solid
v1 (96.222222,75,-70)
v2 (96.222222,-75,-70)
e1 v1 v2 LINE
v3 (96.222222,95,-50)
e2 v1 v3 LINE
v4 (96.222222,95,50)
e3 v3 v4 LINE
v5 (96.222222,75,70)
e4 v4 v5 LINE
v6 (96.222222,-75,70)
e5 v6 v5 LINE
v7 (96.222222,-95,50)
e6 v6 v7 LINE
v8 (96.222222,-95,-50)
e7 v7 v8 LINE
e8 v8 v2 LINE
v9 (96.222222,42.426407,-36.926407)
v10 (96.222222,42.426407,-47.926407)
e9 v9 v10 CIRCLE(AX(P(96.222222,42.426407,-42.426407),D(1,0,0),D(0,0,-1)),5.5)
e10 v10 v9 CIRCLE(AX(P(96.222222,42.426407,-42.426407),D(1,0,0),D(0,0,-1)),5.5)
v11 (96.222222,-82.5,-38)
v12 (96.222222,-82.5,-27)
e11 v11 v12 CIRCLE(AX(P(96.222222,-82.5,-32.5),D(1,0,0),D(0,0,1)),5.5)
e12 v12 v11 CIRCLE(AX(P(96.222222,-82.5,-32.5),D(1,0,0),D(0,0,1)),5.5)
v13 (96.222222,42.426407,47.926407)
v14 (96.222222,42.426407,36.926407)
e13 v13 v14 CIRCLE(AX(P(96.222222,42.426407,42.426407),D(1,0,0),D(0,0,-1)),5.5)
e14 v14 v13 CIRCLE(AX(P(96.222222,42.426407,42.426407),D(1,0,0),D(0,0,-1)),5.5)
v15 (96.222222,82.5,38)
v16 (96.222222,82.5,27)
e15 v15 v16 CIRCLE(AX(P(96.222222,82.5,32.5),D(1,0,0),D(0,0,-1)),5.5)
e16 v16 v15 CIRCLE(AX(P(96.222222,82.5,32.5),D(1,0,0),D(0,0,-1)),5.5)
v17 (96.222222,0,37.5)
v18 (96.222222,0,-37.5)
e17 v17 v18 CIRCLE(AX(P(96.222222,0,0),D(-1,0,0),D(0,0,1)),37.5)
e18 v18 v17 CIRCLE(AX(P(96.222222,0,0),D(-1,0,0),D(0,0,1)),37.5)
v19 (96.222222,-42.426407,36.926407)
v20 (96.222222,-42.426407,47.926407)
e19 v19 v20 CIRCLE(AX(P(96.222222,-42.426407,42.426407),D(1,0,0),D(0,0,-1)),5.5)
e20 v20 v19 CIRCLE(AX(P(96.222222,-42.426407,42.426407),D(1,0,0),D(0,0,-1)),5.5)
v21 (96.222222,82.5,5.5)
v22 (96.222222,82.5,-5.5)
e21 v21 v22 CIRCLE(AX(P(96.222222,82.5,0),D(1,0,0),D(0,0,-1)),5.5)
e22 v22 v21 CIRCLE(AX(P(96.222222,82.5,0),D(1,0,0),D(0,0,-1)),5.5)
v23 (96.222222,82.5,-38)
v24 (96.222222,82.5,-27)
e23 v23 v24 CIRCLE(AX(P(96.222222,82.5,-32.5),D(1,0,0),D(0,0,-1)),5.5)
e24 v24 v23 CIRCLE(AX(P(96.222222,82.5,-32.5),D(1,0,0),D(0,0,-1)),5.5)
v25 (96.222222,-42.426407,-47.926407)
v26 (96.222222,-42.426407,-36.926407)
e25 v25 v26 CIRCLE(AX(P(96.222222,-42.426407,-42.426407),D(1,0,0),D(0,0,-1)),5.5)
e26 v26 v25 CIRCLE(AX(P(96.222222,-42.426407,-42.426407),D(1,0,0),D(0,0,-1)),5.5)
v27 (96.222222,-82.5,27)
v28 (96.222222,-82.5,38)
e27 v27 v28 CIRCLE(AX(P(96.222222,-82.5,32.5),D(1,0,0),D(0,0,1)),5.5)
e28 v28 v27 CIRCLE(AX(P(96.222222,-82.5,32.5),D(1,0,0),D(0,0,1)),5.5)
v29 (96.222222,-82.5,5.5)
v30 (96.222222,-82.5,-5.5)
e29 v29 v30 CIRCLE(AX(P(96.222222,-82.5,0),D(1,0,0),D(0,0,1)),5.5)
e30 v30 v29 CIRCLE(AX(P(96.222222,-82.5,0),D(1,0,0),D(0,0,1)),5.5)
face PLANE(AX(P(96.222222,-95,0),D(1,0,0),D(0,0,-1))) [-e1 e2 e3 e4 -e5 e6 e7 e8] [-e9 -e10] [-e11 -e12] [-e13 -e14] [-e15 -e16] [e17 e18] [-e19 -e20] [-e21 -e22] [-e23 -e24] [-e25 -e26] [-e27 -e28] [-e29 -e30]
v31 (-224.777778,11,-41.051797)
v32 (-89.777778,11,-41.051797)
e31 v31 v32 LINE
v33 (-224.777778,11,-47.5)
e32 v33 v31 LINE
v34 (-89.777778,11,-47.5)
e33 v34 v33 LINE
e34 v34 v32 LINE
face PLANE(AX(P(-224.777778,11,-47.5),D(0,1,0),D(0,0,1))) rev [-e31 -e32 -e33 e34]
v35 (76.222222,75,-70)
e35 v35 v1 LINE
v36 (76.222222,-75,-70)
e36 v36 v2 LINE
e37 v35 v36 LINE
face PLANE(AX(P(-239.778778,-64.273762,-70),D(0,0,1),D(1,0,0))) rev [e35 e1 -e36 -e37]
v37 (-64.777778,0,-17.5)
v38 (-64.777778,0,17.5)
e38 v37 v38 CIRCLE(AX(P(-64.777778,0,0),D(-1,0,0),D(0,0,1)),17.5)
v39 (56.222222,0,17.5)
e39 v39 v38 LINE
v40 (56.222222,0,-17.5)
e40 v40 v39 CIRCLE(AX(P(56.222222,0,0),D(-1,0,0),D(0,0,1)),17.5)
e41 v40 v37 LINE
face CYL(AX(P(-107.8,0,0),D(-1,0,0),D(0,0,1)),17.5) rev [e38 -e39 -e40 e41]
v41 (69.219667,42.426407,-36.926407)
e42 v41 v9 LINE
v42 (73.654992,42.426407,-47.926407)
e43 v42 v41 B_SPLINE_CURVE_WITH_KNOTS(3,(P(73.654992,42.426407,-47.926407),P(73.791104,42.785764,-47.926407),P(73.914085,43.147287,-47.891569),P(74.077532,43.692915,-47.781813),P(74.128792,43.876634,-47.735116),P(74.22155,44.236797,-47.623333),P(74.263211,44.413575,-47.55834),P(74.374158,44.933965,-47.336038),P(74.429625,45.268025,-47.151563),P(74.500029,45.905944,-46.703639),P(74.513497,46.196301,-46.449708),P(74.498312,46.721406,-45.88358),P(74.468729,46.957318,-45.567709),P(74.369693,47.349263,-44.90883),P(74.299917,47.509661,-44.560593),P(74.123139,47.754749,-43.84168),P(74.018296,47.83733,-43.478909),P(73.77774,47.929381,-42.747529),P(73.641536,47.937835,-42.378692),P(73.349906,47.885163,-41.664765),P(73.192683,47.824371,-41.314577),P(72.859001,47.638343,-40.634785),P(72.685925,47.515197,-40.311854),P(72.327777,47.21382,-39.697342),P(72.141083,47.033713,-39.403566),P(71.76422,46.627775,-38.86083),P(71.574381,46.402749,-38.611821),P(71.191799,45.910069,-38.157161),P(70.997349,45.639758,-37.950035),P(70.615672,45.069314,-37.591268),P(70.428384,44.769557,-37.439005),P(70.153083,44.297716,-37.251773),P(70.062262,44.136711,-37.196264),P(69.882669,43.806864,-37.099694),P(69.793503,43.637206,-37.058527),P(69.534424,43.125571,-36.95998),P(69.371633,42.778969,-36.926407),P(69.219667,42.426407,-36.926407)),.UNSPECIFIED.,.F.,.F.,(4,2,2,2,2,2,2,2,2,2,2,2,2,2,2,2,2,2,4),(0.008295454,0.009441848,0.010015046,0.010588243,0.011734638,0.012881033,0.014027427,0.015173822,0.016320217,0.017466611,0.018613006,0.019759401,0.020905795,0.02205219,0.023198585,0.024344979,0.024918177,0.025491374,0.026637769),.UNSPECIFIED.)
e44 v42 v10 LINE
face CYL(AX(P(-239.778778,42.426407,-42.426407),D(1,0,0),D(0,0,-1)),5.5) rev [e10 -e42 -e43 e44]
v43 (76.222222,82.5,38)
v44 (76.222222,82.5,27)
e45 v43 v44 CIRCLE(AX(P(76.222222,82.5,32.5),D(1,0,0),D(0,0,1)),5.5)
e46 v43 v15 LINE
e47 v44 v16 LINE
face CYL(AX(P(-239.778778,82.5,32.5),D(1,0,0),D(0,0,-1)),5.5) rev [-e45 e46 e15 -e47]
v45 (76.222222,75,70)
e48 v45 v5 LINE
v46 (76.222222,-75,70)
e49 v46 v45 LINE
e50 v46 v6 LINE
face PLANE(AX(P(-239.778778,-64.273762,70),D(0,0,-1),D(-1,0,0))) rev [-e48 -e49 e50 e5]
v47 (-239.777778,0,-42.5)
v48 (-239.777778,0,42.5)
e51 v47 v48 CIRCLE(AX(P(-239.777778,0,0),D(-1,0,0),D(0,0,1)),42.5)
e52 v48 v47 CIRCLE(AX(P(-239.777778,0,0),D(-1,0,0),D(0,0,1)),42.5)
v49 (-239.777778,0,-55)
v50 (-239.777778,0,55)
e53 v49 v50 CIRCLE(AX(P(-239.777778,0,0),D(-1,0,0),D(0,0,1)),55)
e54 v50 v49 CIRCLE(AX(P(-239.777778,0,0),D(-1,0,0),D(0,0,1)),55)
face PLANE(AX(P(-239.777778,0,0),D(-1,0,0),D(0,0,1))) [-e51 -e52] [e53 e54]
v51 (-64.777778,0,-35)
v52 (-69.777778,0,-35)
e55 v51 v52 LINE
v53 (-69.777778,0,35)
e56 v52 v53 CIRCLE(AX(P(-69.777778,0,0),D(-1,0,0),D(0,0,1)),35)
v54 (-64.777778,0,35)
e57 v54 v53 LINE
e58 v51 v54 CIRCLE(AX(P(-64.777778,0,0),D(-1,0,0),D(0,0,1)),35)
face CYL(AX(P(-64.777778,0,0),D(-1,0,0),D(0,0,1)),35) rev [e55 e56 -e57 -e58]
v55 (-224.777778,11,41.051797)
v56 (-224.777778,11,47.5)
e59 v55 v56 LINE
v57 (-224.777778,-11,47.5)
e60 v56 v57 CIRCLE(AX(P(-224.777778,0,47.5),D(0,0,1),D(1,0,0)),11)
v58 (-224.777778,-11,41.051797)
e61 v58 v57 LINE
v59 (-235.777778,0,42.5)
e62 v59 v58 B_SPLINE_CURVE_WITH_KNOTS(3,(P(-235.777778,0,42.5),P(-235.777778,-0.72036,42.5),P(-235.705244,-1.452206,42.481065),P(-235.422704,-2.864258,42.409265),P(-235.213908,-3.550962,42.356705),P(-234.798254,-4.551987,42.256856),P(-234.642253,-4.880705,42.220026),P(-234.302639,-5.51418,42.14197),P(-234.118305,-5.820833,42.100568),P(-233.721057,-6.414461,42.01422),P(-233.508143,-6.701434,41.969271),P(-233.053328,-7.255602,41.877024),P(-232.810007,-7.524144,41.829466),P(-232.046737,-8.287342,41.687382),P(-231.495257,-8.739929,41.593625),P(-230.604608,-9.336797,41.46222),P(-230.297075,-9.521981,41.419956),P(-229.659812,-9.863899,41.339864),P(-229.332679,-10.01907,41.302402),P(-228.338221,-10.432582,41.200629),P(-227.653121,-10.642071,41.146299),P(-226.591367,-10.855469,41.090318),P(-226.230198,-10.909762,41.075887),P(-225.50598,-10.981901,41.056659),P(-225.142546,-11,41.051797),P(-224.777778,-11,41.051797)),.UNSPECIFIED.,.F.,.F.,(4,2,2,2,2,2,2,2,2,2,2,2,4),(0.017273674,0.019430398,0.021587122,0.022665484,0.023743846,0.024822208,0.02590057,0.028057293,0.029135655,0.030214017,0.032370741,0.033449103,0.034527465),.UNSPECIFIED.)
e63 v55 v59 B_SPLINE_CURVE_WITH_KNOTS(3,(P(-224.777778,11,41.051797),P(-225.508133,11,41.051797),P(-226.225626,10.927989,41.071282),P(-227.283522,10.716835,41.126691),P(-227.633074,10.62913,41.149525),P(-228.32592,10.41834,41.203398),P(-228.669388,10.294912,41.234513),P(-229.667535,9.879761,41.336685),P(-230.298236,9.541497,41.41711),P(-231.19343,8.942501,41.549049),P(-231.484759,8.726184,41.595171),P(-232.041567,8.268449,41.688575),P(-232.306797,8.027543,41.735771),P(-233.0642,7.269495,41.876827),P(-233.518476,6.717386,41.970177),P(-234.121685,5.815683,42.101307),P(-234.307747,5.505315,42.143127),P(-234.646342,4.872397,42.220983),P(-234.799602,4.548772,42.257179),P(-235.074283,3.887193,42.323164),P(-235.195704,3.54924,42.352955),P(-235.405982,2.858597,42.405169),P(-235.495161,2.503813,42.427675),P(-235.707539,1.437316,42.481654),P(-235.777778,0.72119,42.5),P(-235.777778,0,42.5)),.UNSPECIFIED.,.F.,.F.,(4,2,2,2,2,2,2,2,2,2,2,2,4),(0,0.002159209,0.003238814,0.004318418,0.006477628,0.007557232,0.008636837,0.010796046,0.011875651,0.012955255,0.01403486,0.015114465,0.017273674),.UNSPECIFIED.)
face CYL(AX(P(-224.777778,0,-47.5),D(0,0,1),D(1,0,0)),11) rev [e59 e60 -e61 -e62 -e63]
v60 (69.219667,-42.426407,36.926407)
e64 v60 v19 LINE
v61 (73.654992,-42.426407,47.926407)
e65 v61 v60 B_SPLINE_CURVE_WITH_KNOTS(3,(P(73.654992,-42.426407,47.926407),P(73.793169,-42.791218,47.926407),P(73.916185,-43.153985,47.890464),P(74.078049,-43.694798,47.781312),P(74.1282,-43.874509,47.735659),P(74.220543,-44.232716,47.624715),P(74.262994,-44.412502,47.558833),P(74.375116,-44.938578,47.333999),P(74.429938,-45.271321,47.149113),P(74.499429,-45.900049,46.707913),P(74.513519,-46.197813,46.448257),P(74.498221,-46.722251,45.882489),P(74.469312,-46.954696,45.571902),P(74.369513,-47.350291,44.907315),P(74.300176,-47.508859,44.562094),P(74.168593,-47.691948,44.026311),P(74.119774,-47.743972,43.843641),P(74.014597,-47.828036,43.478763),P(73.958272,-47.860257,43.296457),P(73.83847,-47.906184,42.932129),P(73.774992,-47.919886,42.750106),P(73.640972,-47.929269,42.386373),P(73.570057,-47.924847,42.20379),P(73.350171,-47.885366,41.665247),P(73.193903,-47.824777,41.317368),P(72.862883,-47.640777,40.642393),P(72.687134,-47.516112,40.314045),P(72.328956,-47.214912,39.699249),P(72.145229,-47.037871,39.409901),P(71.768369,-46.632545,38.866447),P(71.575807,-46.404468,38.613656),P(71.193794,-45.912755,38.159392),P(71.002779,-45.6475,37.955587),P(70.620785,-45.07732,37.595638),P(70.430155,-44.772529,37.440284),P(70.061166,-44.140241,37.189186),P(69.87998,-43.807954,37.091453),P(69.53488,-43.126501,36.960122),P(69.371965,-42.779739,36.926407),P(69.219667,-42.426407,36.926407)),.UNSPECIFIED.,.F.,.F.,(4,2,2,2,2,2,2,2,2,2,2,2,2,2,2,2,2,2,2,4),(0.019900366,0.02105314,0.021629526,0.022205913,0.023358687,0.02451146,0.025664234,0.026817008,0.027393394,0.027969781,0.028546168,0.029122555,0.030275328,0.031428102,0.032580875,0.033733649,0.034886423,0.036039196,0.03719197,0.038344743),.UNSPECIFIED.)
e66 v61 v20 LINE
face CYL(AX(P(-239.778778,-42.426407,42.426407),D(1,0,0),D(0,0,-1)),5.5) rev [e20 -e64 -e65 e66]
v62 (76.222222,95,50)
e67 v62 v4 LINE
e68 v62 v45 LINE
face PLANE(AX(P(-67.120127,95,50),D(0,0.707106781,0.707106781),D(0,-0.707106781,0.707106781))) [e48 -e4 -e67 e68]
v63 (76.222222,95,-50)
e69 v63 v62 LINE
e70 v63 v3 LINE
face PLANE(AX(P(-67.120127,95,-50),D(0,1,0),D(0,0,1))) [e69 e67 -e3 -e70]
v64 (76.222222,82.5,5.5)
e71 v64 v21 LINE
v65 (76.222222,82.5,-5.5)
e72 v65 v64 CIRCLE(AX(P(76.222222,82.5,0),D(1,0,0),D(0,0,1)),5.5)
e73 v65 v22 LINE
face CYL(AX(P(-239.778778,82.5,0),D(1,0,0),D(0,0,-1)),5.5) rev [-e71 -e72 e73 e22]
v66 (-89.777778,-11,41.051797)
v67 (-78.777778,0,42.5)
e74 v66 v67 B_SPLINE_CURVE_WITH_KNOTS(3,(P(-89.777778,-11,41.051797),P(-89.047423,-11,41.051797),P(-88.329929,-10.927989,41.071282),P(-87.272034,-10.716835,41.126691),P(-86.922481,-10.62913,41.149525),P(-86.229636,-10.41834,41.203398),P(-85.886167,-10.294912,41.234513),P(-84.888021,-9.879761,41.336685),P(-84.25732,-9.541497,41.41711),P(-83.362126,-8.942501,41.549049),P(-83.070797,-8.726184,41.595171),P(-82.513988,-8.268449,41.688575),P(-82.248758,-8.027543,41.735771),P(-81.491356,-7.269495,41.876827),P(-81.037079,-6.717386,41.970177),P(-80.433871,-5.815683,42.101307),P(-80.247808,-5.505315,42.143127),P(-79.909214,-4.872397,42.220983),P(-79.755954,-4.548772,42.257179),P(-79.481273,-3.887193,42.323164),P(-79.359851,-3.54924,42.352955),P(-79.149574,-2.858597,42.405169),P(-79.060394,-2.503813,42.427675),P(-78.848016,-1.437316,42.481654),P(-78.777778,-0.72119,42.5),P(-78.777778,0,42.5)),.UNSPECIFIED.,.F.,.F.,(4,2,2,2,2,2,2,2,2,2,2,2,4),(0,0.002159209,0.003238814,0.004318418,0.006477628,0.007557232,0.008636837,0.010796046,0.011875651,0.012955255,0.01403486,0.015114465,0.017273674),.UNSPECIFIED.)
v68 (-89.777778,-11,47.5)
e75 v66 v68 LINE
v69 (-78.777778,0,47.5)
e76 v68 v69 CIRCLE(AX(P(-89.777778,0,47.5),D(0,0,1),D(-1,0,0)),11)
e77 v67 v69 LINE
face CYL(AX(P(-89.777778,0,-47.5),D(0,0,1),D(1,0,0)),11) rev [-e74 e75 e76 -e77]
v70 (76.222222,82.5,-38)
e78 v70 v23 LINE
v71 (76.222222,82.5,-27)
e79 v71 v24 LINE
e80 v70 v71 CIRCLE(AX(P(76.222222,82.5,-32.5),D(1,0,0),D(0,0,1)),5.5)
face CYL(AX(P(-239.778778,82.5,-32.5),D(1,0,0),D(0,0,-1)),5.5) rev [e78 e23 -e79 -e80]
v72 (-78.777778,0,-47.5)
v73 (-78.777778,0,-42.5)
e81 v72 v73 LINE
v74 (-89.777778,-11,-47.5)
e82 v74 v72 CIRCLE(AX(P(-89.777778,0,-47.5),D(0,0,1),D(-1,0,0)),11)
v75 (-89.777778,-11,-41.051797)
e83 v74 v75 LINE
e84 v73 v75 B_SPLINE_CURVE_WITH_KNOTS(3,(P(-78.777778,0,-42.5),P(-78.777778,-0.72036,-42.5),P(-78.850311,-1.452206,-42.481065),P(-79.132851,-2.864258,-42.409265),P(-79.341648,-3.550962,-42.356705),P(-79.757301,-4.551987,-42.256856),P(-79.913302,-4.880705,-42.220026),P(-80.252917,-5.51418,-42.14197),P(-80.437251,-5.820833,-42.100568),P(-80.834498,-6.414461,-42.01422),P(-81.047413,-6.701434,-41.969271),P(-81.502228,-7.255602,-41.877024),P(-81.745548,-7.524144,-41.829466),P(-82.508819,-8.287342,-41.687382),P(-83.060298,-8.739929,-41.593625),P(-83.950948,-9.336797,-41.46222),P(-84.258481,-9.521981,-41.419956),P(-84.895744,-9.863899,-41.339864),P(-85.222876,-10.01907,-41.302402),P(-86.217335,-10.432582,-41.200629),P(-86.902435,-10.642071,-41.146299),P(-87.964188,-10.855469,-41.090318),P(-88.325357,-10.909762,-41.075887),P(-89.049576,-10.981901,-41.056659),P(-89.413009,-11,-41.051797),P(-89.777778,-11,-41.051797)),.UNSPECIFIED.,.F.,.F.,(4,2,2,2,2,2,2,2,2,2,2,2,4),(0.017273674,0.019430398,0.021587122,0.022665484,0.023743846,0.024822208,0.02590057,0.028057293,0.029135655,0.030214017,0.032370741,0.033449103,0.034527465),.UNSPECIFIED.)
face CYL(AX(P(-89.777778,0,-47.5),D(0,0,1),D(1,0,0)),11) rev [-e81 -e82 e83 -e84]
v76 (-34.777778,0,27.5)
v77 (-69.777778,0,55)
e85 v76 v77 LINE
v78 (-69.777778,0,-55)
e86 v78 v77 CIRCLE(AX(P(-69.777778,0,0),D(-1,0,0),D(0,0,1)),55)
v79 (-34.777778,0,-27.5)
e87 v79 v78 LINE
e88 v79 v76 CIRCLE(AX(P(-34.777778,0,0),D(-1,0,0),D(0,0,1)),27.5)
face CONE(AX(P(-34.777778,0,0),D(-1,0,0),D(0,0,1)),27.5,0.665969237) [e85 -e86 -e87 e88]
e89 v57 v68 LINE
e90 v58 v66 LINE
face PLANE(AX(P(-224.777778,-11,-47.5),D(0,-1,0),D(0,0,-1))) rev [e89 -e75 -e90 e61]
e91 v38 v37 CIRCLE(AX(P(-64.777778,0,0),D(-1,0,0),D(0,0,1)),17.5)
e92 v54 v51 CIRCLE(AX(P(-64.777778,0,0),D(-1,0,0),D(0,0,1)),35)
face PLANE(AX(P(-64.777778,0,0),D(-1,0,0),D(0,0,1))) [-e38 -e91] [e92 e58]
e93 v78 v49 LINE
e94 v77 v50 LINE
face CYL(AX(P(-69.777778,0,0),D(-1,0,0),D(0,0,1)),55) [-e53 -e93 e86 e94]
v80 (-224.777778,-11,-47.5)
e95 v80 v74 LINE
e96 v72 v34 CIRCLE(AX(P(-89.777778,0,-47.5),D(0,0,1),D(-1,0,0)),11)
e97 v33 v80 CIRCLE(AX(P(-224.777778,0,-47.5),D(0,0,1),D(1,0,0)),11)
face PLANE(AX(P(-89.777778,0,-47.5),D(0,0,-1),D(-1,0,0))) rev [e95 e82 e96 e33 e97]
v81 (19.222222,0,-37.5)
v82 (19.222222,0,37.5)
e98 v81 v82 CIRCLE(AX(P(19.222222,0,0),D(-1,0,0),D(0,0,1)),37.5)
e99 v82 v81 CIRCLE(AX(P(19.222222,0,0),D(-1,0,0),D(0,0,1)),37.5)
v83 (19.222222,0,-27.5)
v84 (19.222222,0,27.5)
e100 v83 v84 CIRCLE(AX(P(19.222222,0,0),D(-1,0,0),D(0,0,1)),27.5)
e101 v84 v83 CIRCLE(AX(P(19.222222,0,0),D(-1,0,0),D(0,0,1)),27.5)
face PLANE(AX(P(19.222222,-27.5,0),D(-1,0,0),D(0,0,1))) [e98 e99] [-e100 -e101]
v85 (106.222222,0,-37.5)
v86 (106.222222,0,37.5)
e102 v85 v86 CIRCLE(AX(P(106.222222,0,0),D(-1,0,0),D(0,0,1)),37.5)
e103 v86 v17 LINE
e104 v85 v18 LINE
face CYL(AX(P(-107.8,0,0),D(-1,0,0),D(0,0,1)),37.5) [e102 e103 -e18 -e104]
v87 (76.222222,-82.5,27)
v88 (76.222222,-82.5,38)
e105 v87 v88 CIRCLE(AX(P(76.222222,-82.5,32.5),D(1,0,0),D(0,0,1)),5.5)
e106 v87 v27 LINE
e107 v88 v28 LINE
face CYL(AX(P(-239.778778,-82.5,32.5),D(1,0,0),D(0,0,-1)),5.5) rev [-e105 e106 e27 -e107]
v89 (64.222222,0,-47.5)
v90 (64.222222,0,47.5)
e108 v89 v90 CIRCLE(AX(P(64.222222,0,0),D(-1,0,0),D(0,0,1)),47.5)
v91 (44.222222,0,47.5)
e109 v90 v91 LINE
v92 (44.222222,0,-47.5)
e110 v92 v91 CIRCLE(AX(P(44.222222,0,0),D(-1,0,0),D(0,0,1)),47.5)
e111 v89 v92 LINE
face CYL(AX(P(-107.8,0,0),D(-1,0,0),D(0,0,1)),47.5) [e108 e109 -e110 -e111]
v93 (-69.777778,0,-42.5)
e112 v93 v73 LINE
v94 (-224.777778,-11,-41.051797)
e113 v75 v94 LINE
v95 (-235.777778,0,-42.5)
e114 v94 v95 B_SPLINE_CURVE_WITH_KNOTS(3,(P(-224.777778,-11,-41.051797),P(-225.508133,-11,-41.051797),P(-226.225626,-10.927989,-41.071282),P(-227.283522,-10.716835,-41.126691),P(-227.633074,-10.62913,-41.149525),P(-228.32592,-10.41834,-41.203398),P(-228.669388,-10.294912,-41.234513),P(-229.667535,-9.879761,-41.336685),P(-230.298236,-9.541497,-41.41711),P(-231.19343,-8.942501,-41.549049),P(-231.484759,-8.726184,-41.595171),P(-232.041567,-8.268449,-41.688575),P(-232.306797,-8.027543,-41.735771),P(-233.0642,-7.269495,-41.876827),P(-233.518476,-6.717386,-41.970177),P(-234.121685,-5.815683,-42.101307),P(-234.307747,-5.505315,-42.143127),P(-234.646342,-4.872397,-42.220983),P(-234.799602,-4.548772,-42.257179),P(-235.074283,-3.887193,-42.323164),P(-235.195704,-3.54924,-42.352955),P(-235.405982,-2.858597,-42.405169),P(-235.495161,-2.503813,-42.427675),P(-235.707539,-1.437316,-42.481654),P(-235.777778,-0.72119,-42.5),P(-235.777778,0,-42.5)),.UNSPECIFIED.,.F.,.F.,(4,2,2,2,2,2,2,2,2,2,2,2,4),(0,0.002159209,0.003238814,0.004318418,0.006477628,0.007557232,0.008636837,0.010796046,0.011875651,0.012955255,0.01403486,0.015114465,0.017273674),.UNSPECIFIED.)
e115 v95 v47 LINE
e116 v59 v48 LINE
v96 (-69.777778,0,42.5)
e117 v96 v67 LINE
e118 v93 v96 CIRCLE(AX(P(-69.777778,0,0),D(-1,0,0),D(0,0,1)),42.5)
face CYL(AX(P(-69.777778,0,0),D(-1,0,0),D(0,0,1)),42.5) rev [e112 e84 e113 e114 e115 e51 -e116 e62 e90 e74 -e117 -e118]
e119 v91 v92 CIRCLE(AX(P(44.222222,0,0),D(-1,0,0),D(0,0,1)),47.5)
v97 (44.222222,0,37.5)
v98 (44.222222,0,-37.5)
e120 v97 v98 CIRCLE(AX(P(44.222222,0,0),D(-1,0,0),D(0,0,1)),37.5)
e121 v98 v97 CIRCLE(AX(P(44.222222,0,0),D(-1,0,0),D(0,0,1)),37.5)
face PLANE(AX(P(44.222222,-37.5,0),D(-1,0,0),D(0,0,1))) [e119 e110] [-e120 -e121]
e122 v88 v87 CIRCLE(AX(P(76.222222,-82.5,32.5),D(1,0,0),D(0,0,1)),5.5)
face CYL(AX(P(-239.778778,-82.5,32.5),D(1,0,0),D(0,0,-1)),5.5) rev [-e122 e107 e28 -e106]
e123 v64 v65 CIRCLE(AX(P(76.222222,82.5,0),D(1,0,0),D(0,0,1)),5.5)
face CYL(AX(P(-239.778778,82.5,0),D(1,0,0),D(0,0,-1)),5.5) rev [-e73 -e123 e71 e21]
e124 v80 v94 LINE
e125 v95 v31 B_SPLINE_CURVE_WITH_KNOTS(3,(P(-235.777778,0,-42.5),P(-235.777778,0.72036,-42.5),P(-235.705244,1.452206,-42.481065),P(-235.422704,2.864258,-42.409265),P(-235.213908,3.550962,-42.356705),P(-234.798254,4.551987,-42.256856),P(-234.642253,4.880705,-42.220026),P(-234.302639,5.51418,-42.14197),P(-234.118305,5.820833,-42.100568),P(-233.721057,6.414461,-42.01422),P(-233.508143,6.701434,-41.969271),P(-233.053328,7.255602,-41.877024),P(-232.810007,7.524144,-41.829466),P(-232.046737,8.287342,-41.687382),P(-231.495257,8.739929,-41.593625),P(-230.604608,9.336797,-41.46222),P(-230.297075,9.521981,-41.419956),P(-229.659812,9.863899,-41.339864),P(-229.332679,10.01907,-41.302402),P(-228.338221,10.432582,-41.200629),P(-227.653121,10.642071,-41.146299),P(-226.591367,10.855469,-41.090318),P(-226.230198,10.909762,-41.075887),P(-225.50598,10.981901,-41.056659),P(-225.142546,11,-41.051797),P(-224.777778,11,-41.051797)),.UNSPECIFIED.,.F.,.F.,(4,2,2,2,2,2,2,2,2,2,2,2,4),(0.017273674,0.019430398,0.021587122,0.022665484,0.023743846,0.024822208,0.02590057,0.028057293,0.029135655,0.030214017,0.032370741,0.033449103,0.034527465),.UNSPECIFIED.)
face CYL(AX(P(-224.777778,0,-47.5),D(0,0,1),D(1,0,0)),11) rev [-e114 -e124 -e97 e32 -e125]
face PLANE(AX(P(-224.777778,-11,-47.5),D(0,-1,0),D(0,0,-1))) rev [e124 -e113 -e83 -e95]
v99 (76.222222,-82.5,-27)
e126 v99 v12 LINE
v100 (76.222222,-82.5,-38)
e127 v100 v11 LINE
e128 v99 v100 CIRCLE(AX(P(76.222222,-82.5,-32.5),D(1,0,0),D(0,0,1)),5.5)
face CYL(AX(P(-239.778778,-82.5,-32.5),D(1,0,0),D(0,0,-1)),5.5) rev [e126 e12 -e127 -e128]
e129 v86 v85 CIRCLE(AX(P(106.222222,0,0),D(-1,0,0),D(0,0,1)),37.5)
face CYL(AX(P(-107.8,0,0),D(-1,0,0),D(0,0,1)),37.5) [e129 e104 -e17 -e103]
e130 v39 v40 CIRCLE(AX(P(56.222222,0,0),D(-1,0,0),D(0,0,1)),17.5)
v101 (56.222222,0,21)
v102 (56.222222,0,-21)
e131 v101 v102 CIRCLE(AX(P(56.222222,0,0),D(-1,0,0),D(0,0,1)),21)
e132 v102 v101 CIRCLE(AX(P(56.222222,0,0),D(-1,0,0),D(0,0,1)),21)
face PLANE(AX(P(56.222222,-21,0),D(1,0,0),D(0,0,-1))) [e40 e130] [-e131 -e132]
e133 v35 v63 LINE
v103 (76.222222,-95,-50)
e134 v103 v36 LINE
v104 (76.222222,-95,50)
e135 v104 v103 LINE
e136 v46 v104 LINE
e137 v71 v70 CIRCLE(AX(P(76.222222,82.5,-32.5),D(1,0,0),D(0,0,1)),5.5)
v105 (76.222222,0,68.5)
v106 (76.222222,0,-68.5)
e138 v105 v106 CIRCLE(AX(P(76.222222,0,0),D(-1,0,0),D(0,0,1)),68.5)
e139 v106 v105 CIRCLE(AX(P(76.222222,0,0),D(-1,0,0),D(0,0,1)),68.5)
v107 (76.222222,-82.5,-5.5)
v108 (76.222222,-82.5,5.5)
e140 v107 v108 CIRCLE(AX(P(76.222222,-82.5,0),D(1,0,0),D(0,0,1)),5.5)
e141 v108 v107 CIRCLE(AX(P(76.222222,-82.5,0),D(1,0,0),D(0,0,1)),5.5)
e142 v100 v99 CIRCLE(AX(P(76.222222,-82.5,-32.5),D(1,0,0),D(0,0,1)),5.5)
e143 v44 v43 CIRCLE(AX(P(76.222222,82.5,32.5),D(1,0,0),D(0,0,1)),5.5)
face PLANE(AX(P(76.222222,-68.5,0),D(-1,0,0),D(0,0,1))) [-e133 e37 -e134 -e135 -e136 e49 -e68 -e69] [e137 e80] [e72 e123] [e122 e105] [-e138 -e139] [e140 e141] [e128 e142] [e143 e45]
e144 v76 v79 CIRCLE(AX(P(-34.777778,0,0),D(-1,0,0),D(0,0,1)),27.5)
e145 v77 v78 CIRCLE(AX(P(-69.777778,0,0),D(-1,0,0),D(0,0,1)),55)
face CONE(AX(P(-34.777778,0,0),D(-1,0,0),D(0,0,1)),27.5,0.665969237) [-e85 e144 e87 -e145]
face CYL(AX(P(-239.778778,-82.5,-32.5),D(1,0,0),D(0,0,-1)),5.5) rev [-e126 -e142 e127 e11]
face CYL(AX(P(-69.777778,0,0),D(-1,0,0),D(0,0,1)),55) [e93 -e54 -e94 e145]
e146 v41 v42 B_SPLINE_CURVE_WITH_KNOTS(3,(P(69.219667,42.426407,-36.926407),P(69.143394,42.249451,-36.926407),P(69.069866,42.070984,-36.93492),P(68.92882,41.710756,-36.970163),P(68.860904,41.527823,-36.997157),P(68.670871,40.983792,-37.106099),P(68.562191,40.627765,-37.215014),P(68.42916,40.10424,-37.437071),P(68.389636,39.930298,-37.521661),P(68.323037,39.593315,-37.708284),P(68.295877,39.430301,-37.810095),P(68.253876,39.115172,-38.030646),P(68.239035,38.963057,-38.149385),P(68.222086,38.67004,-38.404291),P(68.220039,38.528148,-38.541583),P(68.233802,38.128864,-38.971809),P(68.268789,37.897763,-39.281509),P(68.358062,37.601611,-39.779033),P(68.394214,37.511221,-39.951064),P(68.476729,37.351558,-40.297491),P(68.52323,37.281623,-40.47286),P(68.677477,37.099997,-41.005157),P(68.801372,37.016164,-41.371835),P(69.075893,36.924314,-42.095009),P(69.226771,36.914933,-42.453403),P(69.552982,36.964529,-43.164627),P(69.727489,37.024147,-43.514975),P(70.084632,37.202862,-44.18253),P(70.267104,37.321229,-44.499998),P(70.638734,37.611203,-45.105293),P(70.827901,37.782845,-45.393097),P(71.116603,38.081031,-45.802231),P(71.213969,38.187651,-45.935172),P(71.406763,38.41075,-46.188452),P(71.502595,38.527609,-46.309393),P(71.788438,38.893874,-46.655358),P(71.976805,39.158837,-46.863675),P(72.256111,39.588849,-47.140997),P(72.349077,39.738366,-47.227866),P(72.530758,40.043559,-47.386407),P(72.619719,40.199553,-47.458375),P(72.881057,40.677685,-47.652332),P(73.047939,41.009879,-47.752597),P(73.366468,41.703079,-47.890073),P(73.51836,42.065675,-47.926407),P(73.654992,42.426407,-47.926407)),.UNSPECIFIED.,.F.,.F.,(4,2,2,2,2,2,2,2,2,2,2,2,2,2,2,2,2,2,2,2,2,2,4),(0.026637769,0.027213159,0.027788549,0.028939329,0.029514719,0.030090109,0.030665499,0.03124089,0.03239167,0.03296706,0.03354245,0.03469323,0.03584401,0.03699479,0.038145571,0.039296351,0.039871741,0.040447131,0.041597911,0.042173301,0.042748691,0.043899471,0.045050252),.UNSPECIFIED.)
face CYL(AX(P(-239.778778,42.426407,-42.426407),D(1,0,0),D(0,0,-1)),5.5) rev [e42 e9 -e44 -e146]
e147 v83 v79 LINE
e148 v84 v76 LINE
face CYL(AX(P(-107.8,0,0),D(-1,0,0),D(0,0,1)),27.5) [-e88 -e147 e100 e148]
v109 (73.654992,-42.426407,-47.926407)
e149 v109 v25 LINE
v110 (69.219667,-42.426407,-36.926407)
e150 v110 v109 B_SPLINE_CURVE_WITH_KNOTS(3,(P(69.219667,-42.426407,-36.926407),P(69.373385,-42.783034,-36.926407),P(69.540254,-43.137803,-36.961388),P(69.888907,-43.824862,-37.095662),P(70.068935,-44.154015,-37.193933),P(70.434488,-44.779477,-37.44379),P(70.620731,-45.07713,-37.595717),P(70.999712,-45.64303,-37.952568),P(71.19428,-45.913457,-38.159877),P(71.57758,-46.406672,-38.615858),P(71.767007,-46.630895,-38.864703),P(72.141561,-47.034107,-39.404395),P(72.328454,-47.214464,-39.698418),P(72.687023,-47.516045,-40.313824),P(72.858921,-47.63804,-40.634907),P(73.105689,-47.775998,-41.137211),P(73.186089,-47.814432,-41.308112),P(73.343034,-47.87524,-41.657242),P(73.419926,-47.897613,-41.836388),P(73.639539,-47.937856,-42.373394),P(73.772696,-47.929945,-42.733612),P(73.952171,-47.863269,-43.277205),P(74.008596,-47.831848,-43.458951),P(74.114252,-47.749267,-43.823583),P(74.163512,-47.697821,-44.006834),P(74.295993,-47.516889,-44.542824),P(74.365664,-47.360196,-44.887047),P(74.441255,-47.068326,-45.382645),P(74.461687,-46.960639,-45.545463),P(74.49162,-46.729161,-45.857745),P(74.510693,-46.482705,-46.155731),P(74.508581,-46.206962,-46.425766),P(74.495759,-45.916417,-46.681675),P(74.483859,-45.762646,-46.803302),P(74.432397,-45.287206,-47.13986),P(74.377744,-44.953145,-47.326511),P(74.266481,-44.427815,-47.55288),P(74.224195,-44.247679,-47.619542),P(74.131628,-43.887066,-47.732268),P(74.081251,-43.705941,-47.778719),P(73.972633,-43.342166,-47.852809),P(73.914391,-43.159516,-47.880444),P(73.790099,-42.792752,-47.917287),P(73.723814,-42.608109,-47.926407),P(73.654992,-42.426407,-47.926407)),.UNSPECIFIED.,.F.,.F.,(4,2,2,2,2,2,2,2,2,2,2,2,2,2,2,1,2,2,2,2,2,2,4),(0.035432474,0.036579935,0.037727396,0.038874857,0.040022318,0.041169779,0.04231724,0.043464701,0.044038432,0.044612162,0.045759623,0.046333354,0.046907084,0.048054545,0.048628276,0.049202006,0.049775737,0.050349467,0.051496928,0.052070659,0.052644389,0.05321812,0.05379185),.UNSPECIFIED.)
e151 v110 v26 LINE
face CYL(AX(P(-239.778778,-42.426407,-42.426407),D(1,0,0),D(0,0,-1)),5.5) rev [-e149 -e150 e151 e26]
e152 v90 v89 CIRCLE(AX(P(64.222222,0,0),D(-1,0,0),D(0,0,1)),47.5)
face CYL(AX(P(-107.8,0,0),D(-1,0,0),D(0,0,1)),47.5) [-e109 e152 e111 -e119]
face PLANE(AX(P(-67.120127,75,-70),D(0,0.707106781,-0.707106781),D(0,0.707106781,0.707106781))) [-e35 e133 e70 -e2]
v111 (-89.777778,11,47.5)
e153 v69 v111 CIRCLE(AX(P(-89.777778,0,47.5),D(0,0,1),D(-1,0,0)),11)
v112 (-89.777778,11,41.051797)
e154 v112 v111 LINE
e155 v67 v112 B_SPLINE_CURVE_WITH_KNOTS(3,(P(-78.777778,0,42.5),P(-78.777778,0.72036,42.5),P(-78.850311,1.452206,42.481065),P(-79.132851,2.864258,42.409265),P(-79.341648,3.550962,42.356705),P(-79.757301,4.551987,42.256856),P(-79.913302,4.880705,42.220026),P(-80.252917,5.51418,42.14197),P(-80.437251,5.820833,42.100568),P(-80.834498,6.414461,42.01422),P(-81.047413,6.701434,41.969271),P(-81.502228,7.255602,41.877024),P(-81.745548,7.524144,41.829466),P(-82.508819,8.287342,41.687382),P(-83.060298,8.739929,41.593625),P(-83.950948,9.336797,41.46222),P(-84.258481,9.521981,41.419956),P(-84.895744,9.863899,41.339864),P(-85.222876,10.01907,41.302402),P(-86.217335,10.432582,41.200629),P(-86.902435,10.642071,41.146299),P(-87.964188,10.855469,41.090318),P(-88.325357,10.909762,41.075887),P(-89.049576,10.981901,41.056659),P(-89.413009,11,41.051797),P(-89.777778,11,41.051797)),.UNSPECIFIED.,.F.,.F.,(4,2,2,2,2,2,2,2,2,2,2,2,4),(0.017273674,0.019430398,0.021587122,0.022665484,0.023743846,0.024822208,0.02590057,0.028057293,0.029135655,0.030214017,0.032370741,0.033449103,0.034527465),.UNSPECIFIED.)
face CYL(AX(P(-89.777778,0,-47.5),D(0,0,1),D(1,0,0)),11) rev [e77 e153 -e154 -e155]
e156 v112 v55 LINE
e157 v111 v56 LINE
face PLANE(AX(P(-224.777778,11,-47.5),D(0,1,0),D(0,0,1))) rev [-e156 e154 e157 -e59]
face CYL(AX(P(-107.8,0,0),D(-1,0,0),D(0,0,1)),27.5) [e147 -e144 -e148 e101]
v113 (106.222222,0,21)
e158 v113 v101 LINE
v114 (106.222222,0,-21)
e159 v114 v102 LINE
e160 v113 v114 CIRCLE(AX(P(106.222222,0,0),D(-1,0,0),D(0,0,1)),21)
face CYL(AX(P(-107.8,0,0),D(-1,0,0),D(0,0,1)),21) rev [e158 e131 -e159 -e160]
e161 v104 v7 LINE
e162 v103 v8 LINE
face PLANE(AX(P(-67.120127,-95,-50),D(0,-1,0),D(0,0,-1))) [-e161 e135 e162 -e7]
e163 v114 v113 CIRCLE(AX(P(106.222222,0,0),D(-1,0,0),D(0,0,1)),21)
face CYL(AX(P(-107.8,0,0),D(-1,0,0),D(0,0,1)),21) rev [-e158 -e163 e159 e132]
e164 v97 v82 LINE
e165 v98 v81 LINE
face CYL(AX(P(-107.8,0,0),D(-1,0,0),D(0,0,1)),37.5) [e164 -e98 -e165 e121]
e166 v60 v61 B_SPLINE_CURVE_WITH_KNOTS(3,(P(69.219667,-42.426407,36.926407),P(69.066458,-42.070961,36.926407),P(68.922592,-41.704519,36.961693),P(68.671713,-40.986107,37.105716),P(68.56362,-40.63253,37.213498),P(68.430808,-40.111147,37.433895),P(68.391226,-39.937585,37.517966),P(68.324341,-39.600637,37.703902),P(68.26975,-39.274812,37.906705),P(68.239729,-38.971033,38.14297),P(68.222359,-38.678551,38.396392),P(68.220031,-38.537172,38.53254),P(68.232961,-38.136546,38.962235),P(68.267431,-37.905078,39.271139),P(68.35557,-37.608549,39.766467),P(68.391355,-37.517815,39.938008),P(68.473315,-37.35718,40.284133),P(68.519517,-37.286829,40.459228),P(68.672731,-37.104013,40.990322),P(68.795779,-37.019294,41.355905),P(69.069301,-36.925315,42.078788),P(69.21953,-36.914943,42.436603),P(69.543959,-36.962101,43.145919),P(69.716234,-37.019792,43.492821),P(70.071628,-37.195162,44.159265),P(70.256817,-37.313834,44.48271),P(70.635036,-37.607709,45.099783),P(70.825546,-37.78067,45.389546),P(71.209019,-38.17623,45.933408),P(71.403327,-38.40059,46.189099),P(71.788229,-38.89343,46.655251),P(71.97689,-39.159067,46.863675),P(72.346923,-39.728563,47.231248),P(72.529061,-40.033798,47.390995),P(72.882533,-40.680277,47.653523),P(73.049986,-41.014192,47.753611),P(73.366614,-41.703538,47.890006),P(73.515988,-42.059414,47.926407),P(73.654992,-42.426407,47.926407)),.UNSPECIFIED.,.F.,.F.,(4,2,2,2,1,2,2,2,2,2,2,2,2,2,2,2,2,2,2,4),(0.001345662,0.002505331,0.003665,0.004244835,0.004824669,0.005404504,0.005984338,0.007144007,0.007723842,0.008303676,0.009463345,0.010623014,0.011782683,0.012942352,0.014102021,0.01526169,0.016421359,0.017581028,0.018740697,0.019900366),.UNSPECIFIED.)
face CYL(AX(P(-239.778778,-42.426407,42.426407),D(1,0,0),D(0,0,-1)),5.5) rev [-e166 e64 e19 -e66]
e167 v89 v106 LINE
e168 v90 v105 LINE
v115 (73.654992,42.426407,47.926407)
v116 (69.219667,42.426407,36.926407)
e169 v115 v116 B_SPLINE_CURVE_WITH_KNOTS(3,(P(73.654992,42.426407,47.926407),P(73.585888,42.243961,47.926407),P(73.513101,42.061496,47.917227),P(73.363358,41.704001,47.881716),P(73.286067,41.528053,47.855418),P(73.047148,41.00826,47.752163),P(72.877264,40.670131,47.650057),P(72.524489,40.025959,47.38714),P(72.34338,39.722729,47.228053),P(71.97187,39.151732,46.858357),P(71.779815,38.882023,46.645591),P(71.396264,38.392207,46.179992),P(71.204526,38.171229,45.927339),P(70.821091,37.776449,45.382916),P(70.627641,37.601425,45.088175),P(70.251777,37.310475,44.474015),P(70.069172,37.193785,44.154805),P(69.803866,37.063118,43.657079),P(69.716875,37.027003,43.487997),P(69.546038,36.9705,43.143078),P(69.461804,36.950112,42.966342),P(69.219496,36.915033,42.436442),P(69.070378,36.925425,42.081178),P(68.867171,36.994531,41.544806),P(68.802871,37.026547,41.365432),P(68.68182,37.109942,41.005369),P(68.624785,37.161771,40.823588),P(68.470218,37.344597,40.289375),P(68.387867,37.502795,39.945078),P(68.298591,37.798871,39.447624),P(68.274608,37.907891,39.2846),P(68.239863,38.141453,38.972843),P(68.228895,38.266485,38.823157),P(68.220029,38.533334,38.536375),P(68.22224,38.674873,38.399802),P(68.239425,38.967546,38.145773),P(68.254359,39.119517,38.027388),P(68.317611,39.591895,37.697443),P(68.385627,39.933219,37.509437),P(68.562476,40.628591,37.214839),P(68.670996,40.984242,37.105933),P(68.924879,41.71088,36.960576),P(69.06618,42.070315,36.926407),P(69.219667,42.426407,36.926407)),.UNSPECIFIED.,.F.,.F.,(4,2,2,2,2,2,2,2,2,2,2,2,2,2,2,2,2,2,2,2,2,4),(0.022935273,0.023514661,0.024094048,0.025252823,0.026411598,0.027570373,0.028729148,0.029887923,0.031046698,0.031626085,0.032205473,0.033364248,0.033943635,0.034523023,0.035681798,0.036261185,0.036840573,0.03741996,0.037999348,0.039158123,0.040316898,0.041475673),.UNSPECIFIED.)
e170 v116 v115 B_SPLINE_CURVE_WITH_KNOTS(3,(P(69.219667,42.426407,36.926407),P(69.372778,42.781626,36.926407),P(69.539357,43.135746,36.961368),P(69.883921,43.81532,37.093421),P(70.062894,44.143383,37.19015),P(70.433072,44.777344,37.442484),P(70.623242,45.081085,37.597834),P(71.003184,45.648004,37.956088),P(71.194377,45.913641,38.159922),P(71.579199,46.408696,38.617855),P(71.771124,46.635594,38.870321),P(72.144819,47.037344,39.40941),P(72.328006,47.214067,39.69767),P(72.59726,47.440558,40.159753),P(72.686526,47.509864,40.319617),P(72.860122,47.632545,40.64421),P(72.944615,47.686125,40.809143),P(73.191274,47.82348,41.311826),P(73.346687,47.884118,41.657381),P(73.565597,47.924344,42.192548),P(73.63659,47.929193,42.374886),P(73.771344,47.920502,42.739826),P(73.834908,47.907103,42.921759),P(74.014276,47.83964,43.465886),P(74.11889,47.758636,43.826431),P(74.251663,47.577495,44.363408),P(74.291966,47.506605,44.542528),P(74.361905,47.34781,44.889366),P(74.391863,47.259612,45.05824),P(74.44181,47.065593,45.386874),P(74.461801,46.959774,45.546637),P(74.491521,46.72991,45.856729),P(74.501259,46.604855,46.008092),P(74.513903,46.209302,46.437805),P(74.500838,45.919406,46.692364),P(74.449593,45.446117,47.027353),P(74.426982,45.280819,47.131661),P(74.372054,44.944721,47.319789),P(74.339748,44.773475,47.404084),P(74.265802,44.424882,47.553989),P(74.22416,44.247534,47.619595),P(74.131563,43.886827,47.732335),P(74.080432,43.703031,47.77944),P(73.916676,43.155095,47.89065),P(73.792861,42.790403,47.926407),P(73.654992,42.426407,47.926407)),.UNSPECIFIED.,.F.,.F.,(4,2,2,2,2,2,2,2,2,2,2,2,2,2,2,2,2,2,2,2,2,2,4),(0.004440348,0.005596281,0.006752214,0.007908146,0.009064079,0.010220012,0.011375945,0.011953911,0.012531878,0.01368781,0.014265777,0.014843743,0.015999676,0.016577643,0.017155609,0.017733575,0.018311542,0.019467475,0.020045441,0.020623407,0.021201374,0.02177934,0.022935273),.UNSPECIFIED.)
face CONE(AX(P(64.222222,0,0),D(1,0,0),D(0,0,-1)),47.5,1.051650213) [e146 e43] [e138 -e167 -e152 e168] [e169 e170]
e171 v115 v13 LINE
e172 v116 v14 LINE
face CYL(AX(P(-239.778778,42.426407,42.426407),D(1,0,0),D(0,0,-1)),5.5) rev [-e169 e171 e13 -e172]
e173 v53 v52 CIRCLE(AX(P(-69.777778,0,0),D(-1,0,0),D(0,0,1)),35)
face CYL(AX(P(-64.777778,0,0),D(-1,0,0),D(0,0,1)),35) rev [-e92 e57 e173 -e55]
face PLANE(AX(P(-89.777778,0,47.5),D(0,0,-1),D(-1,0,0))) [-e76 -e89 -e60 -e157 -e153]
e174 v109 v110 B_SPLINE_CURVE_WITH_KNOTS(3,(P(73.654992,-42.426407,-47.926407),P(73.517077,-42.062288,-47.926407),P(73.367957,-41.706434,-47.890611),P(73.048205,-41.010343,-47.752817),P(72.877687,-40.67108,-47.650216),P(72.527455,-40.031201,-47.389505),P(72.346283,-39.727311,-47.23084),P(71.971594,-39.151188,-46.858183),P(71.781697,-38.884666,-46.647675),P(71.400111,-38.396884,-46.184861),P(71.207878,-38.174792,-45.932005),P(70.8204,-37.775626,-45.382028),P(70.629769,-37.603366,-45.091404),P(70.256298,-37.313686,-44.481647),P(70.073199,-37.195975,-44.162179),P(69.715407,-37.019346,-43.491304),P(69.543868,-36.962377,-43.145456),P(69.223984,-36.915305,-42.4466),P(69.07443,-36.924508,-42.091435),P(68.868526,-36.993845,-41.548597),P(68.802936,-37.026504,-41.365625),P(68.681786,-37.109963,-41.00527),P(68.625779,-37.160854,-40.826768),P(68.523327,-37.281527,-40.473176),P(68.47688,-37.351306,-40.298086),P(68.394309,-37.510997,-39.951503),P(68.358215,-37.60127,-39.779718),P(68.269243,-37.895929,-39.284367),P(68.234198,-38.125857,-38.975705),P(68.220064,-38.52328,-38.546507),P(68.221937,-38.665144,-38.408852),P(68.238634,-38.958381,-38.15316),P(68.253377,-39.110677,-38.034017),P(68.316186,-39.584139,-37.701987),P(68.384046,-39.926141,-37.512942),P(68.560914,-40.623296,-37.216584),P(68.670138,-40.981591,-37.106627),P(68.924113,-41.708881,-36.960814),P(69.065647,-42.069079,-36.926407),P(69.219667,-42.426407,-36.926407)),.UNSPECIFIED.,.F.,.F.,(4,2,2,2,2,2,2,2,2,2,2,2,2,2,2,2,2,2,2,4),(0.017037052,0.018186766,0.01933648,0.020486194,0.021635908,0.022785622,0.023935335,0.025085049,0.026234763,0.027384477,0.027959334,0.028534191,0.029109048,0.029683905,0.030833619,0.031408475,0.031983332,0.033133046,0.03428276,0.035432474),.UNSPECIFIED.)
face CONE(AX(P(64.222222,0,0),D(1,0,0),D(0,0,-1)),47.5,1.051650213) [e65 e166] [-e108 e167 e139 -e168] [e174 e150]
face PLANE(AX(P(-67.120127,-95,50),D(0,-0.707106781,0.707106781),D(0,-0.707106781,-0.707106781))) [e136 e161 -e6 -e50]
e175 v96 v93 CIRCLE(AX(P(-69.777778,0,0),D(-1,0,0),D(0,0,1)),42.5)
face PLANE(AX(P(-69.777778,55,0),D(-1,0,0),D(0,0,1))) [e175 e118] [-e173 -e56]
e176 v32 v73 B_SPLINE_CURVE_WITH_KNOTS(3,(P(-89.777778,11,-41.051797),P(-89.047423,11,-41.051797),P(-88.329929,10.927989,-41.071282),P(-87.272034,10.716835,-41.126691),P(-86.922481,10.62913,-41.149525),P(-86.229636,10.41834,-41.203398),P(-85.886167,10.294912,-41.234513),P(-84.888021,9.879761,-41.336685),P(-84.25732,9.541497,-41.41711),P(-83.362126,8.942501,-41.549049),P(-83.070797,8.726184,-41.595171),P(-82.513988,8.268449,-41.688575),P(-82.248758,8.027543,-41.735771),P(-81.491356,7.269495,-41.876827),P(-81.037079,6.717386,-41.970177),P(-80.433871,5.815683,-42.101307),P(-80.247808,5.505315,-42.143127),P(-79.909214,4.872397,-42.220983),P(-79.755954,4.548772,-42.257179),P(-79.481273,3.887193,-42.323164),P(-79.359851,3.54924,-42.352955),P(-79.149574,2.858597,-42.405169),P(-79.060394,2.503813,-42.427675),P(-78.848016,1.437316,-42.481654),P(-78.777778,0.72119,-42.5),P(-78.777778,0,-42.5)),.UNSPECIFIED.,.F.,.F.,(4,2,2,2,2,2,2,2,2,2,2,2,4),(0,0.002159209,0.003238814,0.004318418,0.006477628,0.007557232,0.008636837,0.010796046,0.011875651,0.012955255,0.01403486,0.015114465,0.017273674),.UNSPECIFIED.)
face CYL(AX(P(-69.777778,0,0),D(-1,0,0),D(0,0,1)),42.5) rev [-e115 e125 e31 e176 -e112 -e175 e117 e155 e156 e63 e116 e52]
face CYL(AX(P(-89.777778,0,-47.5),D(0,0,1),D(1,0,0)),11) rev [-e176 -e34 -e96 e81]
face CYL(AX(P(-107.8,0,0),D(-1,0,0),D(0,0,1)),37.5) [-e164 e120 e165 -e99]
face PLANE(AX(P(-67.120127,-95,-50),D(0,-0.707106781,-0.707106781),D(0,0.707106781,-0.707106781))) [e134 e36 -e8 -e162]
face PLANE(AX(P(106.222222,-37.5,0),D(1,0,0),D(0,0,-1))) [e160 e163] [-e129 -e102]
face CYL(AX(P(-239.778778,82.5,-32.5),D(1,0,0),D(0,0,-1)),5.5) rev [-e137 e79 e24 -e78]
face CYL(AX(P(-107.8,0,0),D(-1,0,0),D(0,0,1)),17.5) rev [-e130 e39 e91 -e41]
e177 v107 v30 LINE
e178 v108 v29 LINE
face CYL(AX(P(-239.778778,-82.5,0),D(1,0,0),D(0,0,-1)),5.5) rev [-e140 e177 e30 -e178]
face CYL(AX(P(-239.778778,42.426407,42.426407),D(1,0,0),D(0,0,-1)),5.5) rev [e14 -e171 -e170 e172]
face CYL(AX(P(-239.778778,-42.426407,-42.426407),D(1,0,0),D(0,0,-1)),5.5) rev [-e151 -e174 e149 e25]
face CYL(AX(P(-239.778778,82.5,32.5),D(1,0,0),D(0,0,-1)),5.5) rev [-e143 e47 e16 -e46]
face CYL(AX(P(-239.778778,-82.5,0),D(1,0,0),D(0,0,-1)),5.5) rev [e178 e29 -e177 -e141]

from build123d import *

# Parameters (mm, degrees)
CUT_EXTRUDE_1_REACH = 363.865
EXTRUDE_2_DEPTH     = 20
CUT_EXTRUDE_2_REACH = 358.119
SKETCH_4_R          = 5.5
SKETCH_5_R          = 55
SKETCH_5_R_2        = 42.5
EXTRUDE_3_DEPTH     = 170
CUT_EXTRUDE_START   = -175
SKETCH_8_R          = 35
CUT_EXTRUDE_3_DEPTH = 175
CUT_EXTRUDE_4_DEPTH = 47.5


with BuildPart() as part:
    # 草图1 → 旋转1 (revolve)
    with BuildSketch(Plane.XY, mode=Mode.PRIVATE) as revolve_1_sk:
        Polygon((106.222222222, -21), (56.222222222, -21), (56.222222222, -17.5), (-239.777777778, -17.5), (-239.777777778, -30), (-224.777777778, -30), (-224.777777778, -32.5), (-204.777777778, -32.5), (-204.777777778, -35), (-194.777777778, -35), (-187.277777778, -27.5), (19.222222222, -27.5), (19.222222222, -37.5), (44.222222222, -37.5), (44.222222222, -47.5), (64.222222222, -47.5), (76.222222222, -68.5), (76.222222222, -95), (96.222222222, -95), (96.222222222, -37.5), (106.222222222, -37.5), align=None)
    revolve(revolve_1_sk.sketch.rotate(Axis((-107.8, 0, 0), (1, 0, 0)), 270), axis=Axis((-107.8, 0, 0), (1, 0, 0)))

    # 草图2 → 切除-拉伸1 (cut, up to next)
    with BuildSketch(Plane(origin=(96.222222222, 0, 0), x_dir=(0, 0, -1), z_dir=(1, 0, 0)), mode=Mode.PRIVATE) as cut_extrude_1_sk1:
        with BuildLine():
            Line((70, -64.27376204), (70, 64.27376204))
            ThreePointArc((70, 64.27376204), (95.032186583, 0), (70, -64.27376204))
        make_face()
    cut_extrude_1_tool1 = extrude(cut_extrude_1_sk1.sketch, amount=-CUT_EXTRUDE_1_REACH, mode=Mode.PRIVATE) & part.part
    # 草图2 → 切除-拉伸1 (cut, up to next)
    with BuildSketch(Plane(origin=(96.222222222, 0, 0), x_dir=(0, 0, -1), z_dir=(1, 0, 0)), mode=Mode.PRIVATE) as cut_extrude_1_sk2:
        with BuildLine():
            Line((-70, -64.27376204), (-70, 64.27376204))
            ThreePointArc((-70, 64.27376204), (-95.032186583, 0), (-70, -64.27376204))
        make_face()
    cut_extrude_1_tool2 = extrude(cut_extrude_1_sk2.sketch, amount=-CUT_EXTRUDE_1_REACH, mode=Mode.PRIVATE) & part.part
    add(cut_extrude_1_tool1.solids().sort_by_distance((96.222222, 0, -80.135282))[0], mode=Mode.SUBTRACT)
    add(cut_extrude_1_tool2.solids().sort_by_distance((96.222222, 0, 80.135282))[0], mode=Mode.SUBTRACT)

    # 草图3 → 凸台-拉伸2 (add)
    with BuildSketch(Plane(origin=(96.222222222, 0, 0), x_dir=(0, 0, -1), z_dir=(1, 0, 0))):
        with BuildLine():
            Line((-70, 75), (-70, 64.226162893))
            ThreePointArc((-70, 64.226162893), (-38.232934266, 86.96690599), (0, 95))
            Line((0, 95), (-50, 95))
            Line((-50, 95), (-70, 75))
        make_face()
        with BuildLine():
            ThreePointArc((0, 95), (38.232934266, 86.96690599), (70, 64.226162893))
            Line((70, 64.226162893), (70, 75))
            Line((70, 75), (50, 95))
            Line((50, 95), (0, 95))
        make_face()
        with BuildLine():
            ThreePointArc((0, -95), (-38.232934266, -86.96690599), (-70, -64.226162893))
            Line((-70, -64.226162893), (-70, -75))
            Line((-70, -75), (-50, -95))
            Line((-50, -95), (0, -95))
        make_face()
        with BuildLine():
            Line((70, -75), (70, -64.226162893))
            ThreePointArc((70, -64.226162893), (38.232934266, -86.96690599), (0, -95))
            Line((0, -95), (50, -95))
            Line((50, -95), (70, -75))
        make_face()
    extrude(amount=-EXTRUDE_2_DEPTH)

    # 草图4 → 切除-拉伸2 (cut, up to next)
    with BuildSketch(Plane(origin=(96.222222222, 0, 0), x_dir=(0, 0, -1), z_dir=(1, 0, 0)), mode=Mode.PRIVATE) as cut_extrude_2_sk1:
        with Locations((42.426406871, 42.426406871)):
            Circle(SKETCH_4_R)
    cut_extrude_2_tool1 = extrude(cut_extrude_2_sk1.sketch, amount=-CUT_EXTRUDE_2_REACH, mode=Mode.PRIVATE) & part.part
    # 草图4 → 切除-拉伸2 (cut, up to next)
    with BuildSketch(Plane(origin=(96.222222222, 0, 0), x_dir=(0, 0, -1), z_dir=(1, 0, 0)), mode=Mode.PRIVATE) as cut_extrude_2_sk2:
        with Locations((42.426406871, -42.426406871)):
            Circle(SKETCH_4_R)
    cut_extrude_2_tool2 = extrude(cut_extrude_2_sk2.sketch, amount=-CUT_EXTRUDE_2_REACH, mode=Mode.PRIVATE) & part.part
    # 草图4 → 切除-拉伸2 (cut, up to next)
    with BuildSketch(Plane(origin=(96.222222222, 0, 0), x_dir=(0, 0, -1), z_dir=(1, 0, 0)), mode=Mode.PRIVATE) as cut_extrude_2_sk3:
        with Locations((-42.426406871, -42.426406871)):
            Circle(SKETCH_4_R)
    cut_extrude_2_tool3 = extrude(cut_extrude_2_sk3.sketch, amount=-CUT_EXTRUDE_2_REACH, mode=Mode.PRIVATE) & part.part
    # 草图4 → 切除-拉伸2 (cut, up to next)
    with BuildSketch(Plane(origin=(96.222222222, 0, 0), x_dir=(0, 0, -1), z_dir=(1, 0, 0)), mode=Mode.PRIVATE) as cut_extrude_2_sk4:
        with Locations((-42.426406871, 42.426406871)):
            Circle(SKETCH_4_R)
    cut_extrude_2_tool4 = extrude(cut_extrude_2_sk4.sketch, amount=-CUT_EXTRUDE_2_REACH, mode=Mode.PRIVATE) & part.part
    # 草图4 → 切除-拉伸2 (cut, up to next)
    with BuildSketch(Plane(origin=(96.222222222, 0, 0), x_dir=(0, 0, -1), z_dir=(1, 0, 0)), mode=Mode.PRIVATE) as cut_extrude_2_sk5:
        with Locations((0, 82.5)):
            Circle(SKETCH_4_R)
    cut_extrude_2_tool5 = extrude(cut_extrude_2_sk5.sketch, amount=-CUT_EXTRUDE_2_REACH, mode=Mode.PRIVATE) & part.part
    # 草图4 → 切除-拉伸2 (cut, up to next)
    with BuildSketch(Plane(origin=(96.222222222, 0, 0), x_dir=(0, 0, -1), z_dir=(1, 0, 0)), mode=Mode.PRIVATE) as cut_extrude_2_sk6:
        with Locations((-32.5, 82.5)):
            Circle(SKETCH_4_R)
    cut_extrude_2_tool6 = extrude(cut_extrude_2_sk6.sketch, amount=-CUT_EXTRUDE_2_REACH, mode=Mode.PRIVATE) & part.part
    # 草图4 → 切除-拉伸2 (cut, up to next)
    with BuildSketch(Plane(origin=(96.222222222, 0, 0), x_dir=(0, 0, -1), z_dir=(1, 0, 0)), mode=Mode.PRIVATE) as cut_extrude_2_sk7:
        with Locations((32.5, 82.5)):
            Circle(SKETCH_4_R)
    cut_extrude_2_tool7 = extrude(cut_extrude_2_sk7.sketch, amount=-CUT_EXTRUDE_2_REACH, mode=Mode.PRIVATE) & part.part
    # 草图4 → 切除-拉伸2 (cut, up to next)
    with BuildSketch(Plane(origin=(96.222222222, 0, 0), x_dir=(0, 0, -1), z_dir=(1, 0, 0)), mode=Mode.PRIVATE) as cut_extrude_2_sk8:
        with Locations(Location((32.5, -82.5, 0), (0, 0, 180))):
            Circle(SKETCH_4_R)
    cut_extrude_2_tool8 = extrude(cut_extrude_2_sk8.sketch, amount=-CUT_EXTRUDE_2_REACH, mode=Mode.PRIVATE) & part.part
    # 草图4 → 切除-拉伸2 (cut, up to next)
    with BuildSketch(Plane(origin=(96.222222222, 0, 0), x_dir=(0, 0, -1), z_dir=(1, 0, 0)), mode=Mode.PRIVATE) as cut_extrude_2_sk9:
        with Locations(Location((0, -82.5, 0), (0, 0, 180))):
            Circle(SKETCH_4_R)
    cut_extrude_2_tool9 = extrude(cut_extrude_2_sk9.sketch, amount=-CUT_EXTRUDE_2_REACH, mode=Mode.PRIVATE) & part.part
    # 草图4 → 切除-拉伸2 (cut, up to next)
    with BuildSketch(Plane(origin=(96.222222222, 0, 0), x_dir=(0, 0, -1), z_dir=(1, 0, 0)), mode=Mode.PRIVATE) as cut_extrude_2_sk10:
        with Locations(Location((-32.5, -82.5, 0), (0, 0, 180))):
            Circle(SKETCH_4_R)
    cut_extrude_2_tool10 = extrude(cut_extrude_2_sk10.sketch, amount=-CUT_EXTRUDE_2_REACH, mode=Mode.PRIVATE) & part.part
    add(cut_extrude_2_tool1.solids().sort_by_distance((96.222222, 42.426407, -42.426407))[0], mode=Mode.SUBTRACT)
    add(cut_extrude_2_tool2.solids().sort_by_distance((96.222222, -42.426407, -42.426407))[0], mode=Mode.SUBTRACT)
    add(cut_extrude_2_tool3.solids().sort_by_distance((96.222222, -42.426407, 42.426407))[0], mode=Mode.SUBTRACT)
    add(cut_extrude_2_tool4.solids().sort_by_distance((96.222222, 42.426407, 42.426407))[0], mode=Mode.SUBTRACT)
    add(cut_extrude_2_tool5.solids().sort_by_distance((96.222222, 82.5, 0))[0], mode=Mode.SUBTRACT)
    add(cut_extrude_2_tool6.solids().sort_by_distance((96.222222, 82.5, 32.5))[0], mode=Mode.SUBTRACT)
    add(cut_extrude_2_tool7.solids().sort_by_distance((96.222222, 82.5, -32.5))[0], mode=Mode.SUBTRACT)
    add(cut_extrude_2_tool8.solids().sort_by_distance((96.222222, -82.5, -32.5))[0], mode=Mode.SUBTRACT)
    add(cut_extrude_2_tool9.solids().sort_by_distance((96.222222, -82.5, 0))[0], mode=Mode.SUBTRACT)
    add(cut_extrude_2_tool10.solids().sort_by_distance((96.222222, -82.5, 32.5))[0], mode=Mode.SUBTRACT)



with BuildPart() as body_2:
    # 草图5 → 凸台-拉伸3 (new body)
    with BuildSketch(Plane.ZY.offset(239.777777778)):
        Circle(SKETCH_5_R)
        Circle(SKETCH_5_R_2, mode=Mode.SUBTRACT)
    extrude(amount=-EXTRUDE_3_DEPTH)


with BuildPart() as part_1:
    add(part.part)

    add(body_2.part)  # 旋转2 merges body 2
    # 草图7 → 旋转2 (revolve)
    with BuildSketch(Plane.XY, mode=Mode.PRIVATE) as revolve_2_sk:
        Polygon((-69.777777778, 55), (-69.777777778, 27.5), (-34.777777778, 27.5), align=None)
    revolve(revolve_2_sk.sketch.rotate(Axis((-69.777777778, 0, 0), (-1, 0, 0)), 270), axis=Axis((-69.777777778, 0, 0), (-1, 0, 0)))

    # 草图8 → 切除-拉伸3 (cut)
    with BuildSketch(Plane.ZY.offset(239.777777778).offset(CUT_EXTRUDE_START)):
        Circle(SKETCH_8_R)
    extrude(amount=CUT_EXTRUDE_3_DEPTH, mode=Mode.SUBTRACT)

    # 草图9 → 切除-拉伸4 (cut, symmetric)
    with BuildSketch(Plane.XY):
        with BuildLine():
            Line((-224.777777778, 11), (-89.777777778, 11))
            ThreePointArc((-89.777777778, 11), (-78.777777778, 0), (-89.777777778, -11))
            Line((-89.777777778, -11), (-224.777777778, -11))
            ThreePointArc((-224.777777778, -11), (-235.777777778, 0), (-224.777777778, 11))
        make_face()
    extrude(amount=CUT_EXTRUDE_4_DEPTH, both=True, mode=Mode.SUBTRACT)


solid = part_1.part
